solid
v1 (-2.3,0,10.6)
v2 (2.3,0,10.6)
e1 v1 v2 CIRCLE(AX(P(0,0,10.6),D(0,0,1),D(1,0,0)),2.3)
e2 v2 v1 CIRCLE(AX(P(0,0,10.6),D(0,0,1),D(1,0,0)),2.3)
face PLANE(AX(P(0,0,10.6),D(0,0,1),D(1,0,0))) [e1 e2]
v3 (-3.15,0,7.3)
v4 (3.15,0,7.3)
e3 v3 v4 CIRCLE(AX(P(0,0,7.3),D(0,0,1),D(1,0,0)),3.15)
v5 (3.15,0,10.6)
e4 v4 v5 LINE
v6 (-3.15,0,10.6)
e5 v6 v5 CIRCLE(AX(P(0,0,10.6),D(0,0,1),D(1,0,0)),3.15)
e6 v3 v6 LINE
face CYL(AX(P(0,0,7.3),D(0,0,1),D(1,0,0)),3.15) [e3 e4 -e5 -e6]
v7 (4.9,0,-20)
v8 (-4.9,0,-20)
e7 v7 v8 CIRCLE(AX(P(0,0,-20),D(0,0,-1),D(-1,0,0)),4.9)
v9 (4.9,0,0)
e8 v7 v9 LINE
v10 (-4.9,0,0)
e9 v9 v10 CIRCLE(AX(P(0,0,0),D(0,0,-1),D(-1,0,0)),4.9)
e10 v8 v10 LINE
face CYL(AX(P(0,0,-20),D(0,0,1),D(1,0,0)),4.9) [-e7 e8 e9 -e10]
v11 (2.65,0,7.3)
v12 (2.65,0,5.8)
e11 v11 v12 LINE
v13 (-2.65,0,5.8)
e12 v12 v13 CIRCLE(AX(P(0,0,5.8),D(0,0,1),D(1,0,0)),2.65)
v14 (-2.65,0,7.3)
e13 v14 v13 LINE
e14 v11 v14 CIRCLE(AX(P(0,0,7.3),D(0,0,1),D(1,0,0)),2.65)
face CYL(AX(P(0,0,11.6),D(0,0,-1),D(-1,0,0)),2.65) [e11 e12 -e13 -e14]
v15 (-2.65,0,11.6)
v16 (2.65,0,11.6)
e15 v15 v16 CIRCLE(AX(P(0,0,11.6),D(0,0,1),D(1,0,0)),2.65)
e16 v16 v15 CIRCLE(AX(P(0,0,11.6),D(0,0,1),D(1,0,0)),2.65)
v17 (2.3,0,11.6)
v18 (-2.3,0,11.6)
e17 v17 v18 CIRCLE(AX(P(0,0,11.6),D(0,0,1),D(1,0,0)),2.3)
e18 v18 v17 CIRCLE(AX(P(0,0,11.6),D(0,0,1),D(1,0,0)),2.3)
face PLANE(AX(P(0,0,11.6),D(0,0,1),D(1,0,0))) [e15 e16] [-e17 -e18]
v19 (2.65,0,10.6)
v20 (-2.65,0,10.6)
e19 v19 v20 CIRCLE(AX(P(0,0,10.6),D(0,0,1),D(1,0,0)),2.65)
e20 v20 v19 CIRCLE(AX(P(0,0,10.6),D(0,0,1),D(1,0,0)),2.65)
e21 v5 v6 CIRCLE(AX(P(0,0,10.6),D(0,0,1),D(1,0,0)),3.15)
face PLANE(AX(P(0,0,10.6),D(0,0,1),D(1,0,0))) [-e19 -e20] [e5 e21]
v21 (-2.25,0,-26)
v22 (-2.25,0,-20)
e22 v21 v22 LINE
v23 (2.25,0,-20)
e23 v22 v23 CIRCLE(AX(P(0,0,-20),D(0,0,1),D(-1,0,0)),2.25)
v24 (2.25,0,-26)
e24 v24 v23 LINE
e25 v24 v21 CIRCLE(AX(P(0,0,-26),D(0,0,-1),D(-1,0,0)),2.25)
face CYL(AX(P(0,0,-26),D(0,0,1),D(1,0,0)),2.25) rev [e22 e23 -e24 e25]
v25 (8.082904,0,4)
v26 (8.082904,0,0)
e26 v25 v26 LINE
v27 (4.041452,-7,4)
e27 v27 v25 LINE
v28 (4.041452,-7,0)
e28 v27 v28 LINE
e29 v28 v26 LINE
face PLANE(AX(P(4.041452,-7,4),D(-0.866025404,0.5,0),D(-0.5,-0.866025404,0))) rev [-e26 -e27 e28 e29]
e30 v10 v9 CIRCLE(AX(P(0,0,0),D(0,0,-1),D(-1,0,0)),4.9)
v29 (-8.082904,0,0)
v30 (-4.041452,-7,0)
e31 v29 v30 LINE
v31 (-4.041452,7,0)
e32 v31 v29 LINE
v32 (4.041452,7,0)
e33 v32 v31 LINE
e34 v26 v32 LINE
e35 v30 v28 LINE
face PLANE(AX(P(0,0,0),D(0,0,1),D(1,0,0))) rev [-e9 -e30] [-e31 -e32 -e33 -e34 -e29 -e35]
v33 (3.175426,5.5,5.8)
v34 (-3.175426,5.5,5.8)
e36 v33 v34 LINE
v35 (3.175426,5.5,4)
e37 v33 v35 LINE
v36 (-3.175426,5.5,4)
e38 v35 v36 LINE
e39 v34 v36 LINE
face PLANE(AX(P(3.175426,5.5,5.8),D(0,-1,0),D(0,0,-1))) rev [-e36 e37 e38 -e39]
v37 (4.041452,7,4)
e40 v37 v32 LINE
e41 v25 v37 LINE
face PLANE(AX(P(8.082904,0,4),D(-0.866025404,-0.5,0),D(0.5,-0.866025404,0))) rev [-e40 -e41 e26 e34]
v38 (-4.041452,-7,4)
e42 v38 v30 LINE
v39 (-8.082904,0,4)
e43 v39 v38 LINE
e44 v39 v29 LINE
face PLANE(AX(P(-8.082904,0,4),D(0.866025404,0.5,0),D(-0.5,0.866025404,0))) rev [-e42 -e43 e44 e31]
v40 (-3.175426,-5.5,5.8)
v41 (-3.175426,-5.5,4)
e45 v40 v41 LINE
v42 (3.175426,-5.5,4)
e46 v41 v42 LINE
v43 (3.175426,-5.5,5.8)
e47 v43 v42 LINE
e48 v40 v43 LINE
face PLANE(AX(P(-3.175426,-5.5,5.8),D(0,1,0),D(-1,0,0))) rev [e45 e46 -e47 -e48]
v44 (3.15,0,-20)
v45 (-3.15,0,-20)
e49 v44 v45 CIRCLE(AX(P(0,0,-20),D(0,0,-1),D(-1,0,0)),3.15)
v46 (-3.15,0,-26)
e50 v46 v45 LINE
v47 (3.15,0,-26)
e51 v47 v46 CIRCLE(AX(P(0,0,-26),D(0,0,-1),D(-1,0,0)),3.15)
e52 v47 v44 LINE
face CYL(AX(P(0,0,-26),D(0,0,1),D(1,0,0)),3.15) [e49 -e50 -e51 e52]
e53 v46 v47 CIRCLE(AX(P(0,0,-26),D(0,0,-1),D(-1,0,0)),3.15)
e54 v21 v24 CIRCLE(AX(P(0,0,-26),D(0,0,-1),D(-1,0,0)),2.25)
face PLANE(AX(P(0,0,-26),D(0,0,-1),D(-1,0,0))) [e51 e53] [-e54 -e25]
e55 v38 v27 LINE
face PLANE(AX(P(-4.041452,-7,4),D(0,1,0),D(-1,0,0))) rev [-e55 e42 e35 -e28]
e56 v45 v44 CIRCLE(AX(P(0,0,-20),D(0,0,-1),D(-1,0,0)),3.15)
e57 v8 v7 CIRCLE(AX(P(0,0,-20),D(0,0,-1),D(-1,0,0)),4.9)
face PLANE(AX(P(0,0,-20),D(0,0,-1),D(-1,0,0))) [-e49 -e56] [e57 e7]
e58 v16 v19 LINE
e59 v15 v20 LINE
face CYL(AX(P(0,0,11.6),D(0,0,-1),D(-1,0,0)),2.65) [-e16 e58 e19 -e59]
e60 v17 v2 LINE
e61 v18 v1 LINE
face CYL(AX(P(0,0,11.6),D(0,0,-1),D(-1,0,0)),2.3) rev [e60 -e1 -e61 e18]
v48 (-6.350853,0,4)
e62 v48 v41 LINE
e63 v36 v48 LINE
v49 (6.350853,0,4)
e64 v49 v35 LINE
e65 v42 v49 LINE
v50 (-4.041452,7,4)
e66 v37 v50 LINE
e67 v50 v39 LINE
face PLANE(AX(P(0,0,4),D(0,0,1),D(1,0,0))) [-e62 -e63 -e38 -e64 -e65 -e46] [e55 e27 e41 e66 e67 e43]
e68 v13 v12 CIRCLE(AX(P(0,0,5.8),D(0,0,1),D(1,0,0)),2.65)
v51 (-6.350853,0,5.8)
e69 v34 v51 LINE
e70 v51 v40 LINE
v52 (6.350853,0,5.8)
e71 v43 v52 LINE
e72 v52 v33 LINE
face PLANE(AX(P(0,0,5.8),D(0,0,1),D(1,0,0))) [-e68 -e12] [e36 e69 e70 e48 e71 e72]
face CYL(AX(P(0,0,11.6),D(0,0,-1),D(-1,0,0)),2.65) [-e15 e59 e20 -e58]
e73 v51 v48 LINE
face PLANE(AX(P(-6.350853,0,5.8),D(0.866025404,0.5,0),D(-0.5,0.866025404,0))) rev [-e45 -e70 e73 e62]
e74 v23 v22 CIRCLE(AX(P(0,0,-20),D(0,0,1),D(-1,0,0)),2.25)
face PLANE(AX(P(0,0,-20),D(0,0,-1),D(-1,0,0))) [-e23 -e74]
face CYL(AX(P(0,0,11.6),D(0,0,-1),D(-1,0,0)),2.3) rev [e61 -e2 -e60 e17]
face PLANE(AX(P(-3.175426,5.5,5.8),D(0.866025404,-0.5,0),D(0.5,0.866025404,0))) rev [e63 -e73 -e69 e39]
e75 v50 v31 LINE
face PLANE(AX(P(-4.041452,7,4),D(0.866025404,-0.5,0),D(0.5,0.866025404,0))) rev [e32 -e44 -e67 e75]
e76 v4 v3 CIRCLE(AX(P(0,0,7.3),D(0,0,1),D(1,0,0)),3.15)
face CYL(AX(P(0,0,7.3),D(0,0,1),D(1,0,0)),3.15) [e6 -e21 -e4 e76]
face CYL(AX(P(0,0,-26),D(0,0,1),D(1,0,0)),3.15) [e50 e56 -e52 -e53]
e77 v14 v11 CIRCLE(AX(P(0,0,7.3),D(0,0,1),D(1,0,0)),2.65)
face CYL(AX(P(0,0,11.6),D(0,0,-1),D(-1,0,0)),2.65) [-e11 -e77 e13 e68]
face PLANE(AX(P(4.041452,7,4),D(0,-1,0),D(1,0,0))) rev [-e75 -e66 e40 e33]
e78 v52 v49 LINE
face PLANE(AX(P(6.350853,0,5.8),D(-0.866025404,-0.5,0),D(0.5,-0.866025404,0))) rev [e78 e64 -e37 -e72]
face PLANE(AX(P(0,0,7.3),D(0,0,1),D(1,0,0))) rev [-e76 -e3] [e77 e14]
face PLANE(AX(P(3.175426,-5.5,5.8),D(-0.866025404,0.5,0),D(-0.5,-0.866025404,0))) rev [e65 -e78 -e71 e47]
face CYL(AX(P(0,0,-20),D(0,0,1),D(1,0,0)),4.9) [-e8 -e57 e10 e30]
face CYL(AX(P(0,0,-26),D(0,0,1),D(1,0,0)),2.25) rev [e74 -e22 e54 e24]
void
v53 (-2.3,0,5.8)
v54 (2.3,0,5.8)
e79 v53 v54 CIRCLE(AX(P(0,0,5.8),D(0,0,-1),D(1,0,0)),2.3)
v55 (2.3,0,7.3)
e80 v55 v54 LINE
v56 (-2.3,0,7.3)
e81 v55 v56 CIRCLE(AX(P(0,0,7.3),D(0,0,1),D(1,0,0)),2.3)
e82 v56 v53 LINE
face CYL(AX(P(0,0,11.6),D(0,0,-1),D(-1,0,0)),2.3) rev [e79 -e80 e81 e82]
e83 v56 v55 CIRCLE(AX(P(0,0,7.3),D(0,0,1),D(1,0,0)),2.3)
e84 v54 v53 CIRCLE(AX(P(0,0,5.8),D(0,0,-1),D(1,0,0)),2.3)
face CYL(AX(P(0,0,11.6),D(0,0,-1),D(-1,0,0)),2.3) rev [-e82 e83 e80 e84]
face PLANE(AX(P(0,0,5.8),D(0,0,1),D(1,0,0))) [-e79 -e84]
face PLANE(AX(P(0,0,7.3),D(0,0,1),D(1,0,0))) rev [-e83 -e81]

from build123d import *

# Parameters (mm, degrees)
BOSS_EXTRUDE1_DEPTH = 4
BOSS_EXTRUDE2_DEPTH = 1.8
SKETCH3_R           = 2.65
SKETCH3_R_2         = 2.3
BOSS_EXTRUDE3_DEPTH = 5.8
BOSS_EXTRUDE4_START = -1
SKETCH4_R           = 3.15
BOSS_EXTRUDE4_DEPTH = 3.3
SKETCH5_R           = 4.9
BOSS_EXTRUDE5_DEPTH = 20
SKETCH6_R           = 3.15
SKETCH6_R_2         = 2.25
BOSS_EXTRUDE6_DEPTH = 6


with BuildPart() as part:
    # Sketch1 → Boss-Extrude1 (new body)
    with BuildSketch(Plane.XY):
        Polygon((8.082903769, 0), (4.041451884, 7), (-4.041451884, 7), (-8.082903769, 0), (-4.041451884, -7), (4.041451884, -7), align=None)
    extrude(amount=BOSS_EXTRUDE1_DEPTH)

    # Sketch2 → Boss-Extrude2 (add)
    with BuildSketch(Plane.XY.offset(4)):
        Polygon((6.350852961, 0), (3.175426481, 5.5), (-3.175426481, 5.5), (-6.350852961, 0), (-3.175426481, -5.5), (3.175426481, -5.5), align=None)
    extrude(amount=BOSS_EXTRUDE2_DEPTH)

    # Sketch3 → Boss-Extrude3 (add)
    with BuildSketch(Plane.XY.offset(5.8)):
        Circle(SKETCH3_R)
        Circle(SKETCH3_R_2, mode=Mode.SUBTRACT)
    extrude(amount=BOSS_EXTRUDE3_DEPTH)

    # Sketch4 → Boss-Extrude4 (add)
    with BuildSketch(Plane.XY.offset(11.6).offset(BOSS_EXTRUDE4_START)):
        Circle(SKETCH4_R)
    extrude(amount=-BOSS_EXTRUDE4_DEPTH)

    # Sketch5 → Boss-Extrude5 (add)
    with BuildSketch(Plane(origin=(0, 0, 0), x_dir=(-1, 0, 0), z_dir=(0, 0, -1))):
        Circle(SKETCH5_R)
    extrude(amount=BOSS_EXTRUDE5_DEPTH)

    # Sketch6 → Boss-Extrude6 (add)
    with BuildSketch(Plane(origin=(0, 0, -20), x_dir=(-1, 0, 0), z_dir=(0, 0, -1))):
        with Locations(Location((0, 0, 0), (0, 0, 180))):
            Circle(SKETCH6_R)
        Circle(SKETCH6_R_2, mode=Mode.SUBTRACT)
    extrude(amount=BOSS_EXTRUDE6_DEPTH)


solid = part.part
